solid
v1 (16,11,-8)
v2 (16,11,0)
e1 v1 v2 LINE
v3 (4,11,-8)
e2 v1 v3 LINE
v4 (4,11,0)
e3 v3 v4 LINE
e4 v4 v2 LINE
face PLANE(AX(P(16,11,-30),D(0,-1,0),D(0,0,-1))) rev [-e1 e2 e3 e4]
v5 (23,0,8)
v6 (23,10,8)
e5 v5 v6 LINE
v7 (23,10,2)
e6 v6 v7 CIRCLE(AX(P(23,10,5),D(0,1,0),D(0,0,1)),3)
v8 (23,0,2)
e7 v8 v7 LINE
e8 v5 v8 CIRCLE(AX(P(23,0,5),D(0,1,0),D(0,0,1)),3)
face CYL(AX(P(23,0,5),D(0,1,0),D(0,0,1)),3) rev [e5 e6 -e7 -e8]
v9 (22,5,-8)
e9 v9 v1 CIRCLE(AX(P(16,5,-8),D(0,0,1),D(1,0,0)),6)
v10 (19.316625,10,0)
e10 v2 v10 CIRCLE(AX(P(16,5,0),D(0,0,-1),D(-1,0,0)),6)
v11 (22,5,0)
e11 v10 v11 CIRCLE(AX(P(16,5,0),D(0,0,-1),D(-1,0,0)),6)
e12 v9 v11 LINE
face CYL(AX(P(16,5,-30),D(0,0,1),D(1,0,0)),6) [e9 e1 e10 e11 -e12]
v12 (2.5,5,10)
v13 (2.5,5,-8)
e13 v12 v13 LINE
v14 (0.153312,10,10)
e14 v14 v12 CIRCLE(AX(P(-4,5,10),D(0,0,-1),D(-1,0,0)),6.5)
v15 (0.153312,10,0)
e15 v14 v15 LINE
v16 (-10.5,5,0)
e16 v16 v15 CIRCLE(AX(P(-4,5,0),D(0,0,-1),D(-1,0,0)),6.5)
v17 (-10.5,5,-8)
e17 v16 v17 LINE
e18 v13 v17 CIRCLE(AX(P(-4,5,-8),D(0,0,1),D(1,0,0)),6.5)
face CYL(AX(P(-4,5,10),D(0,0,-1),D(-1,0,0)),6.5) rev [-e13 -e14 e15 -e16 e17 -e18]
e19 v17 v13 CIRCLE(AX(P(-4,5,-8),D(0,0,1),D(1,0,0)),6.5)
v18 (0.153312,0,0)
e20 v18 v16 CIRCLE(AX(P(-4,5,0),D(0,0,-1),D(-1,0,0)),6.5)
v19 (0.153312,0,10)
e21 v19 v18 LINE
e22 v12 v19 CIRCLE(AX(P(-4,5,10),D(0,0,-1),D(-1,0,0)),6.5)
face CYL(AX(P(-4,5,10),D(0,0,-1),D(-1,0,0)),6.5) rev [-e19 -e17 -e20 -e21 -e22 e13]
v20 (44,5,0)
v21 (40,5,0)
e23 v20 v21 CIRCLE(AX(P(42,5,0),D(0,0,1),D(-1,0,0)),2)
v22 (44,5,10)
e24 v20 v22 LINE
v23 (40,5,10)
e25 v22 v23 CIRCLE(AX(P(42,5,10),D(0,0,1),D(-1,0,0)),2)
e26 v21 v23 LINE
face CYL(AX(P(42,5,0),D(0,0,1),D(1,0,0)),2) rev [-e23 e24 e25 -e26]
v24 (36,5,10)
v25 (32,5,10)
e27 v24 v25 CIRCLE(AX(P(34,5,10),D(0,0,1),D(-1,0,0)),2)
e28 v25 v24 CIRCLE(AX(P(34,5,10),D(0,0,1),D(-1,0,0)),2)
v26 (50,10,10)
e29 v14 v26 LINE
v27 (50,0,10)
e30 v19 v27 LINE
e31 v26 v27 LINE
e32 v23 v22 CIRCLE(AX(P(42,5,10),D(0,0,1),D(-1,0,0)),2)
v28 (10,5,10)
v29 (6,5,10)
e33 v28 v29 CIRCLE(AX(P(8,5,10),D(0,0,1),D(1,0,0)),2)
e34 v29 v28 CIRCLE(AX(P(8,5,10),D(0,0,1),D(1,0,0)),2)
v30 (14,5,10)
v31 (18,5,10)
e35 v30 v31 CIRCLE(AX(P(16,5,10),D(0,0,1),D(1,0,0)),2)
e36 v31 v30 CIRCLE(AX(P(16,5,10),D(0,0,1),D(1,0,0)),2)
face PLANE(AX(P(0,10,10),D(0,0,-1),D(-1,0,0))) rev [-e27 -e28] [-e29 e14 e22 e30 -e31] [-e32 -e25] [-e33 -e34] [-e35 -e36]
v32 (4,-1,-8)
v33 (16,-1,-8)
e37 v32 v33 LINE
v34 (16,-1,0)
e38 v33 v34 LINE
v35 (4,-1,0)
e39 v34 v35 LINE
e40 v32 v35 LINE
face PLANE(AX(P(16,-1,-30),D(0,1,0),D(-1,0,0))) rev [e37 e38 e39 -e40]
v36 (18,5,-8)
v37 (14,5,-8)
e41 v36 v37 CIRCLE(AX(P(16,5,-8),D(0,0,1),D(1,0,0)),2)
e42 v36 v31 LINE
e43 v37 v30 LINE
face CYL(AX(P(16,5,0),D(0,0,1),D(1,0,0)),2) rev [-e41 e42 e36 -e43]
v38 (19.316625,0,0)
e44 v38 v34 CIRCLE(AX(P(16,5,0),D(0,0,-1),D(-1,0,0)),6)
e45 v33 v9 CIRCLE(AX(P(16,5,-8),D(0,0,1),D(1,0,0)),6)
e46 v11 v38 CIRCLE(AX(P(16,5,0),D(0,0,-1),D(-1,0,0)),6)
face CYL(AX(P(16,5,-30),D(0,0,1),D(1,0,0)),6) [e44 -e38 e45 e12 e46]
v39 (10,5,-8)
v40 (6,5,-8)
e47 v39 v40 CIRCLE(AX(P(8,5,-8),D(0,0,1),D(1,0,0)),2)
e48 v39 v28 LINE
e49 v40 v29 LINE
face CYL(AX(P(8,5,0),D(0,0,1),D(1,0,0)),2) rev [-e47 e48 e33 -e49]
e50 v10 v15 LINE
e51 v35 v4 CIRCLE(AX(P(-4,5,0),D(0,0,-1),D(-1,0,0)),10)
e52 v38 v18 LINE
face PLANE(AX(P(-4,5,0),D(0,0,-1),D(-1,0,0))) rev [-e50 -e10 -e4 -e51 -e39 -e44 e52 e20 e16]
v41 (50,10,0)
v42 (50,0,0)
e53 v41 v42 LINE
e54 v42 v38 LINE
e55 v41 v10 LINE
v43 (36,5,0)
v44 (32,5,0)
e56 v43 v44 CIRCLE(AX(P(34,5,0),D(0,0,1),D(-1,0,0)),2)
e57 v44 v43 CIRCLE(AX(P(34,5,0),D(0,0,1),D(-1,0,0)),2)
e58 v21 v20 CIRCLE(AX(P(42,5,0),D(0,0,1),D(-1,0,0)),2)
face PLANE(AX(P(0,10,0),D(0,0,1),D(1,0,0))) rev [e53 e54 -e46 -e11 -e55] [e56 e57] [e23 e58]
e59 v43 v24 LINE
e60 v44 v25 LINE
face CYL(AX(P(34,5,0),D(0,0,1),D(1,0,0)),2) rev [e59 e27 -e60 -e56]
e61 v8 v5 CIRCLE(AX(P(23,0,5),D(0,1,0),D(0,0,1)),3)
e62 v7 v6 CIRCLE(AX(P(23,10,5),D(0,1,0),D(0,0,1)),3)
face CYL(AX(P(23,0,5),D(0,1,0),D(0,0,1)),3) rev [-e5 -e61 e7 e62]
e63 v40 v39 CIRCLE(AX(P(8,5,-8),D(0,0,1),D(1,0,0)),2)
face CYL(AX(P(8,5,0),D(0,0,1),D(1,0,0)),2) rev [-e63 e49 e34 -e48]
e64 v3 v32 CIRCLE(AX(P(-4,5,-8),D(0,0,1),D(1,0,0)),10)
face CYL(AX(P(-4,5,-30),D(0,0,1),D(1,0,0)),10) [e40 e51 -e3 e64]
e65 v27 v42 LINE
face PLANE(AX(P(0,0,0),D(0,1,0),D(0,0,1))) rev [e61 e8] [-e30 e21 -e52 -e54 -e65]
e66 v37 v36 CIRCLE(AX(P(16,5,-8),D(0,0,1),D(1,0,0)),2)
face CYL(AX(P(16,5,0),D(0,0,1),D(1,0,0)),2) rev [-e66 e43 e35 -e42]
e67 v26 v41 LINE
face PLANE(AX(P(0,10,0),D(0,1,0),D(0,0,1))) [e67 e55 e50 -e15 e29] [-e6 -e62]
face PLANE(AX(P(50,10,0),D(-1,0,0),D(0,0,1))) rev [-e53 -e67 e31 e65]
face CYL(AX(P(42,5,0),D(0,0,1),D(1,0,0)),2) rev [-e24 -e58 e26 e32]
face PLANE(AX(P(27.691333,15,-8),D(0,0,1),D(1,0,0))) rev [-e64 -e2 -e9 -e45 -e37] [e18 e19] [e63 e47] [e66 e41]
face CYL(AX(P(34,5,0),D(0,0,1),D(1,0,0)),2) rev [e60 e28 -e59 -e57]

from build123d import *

# Parameters (mm, degrees)
SKETCH1_W               = 50
SKETCH1_H               = 10
BOSS_EXTRUDE1_DEPTH     = 10
SKETCH2_R               = 3
CUT_EXTRUDE1_DEPTH      = 10
SKETCH3_R               = 2
CUT_EXTRUDE2_DEPTH      = 10
BOSS_EXTRUDE2_DEPTH     = 30
CUT_EXTRUDE4_DEPTH      = 61.464865831
CUT_EXTRUDE4_DEPTH_BACK = 61.464865831
SKETCH6_W               = 47
SKETCH6_H               = 25
CUT_EXTRUDE5_DEPTH      = 54.150729064
CUT_EXTRUDE5_DEPTH_BACK = 54.150729064
SKETCH7_R               = 2
SKETCH5_R               = 6.5
CUT_EXTRUDE6_DEPTH      = 66.76473219


with BuildPart() as part:
    # Sketch1 → Boss-Extrude1 (new body)
    with BuildSketch(Plane(origin=(0, 0, 0), x_dir=(1, 0, 0), z_dir=(0, 1, 0))):
        with Locations((25, -5)):
            Rectangle(SKETCH1_W, SKETCH1_H)
    extrude(amount=BOSS_EXTRUDE1_DEPTH)

    # Sketch2 → Cut-Extrude1 (cut)
    with BuildSketch(Plane(origin=(0, 10, 0), x_dir=(1, 0, 0), z_dir=(0, 1, 0))):
        with Locations(Location((23, -5, 0), (0, 0, 270))):
            Circle(SKETCH2_R)
    extrude(amount=-CUT_EXTRUDE1_DEPTH, mode=Mode.SUBTRACT)

    # Sketch3 → Cut-Extrude2 (cut)
    with BuildSketch(Plane.XY.offset(10)):
        with Locations((8, 5)):
            Circle(SKETCH3_R)
        with Locations((16, 5)):
            Circle(SKETCH3_R)
        with Locations(Location((42, 5, 0), (0, 0, 180))):
            Circle(SKETCH3_R)
        with Locations(Location((34, 5, 0), (0, 0, 180))):
            Circle(SKETCH3_R)
    extrude(amount=-CUT_EXTRUDE2_DEPTH, mode=Mode.SUBTRACT)

    # Sketch4 → Boss-Extrude2 (add)
    with BuildSketch(Plane(origin=(0, 0, 0), x_dir=(-1, 0, 0), z_dir=(0, 0, -1))):
        with BuildLine():
            Line((-16, 11), (-4, 11))
            ThreePointArc((-4, 11), (14, 5), (-4, -1))
            Line((-4, -1), (-16, -1))
            ThreePointArc((-16, -1), (-22, 5), (-16, 11))
        make_face()
    extrude(amount=BOSS_EXTRUDE2_DEPTH)

    # Sketch6 → Cut-Extrude4 (cut, two sides: drawn at the far end of the back side and taken through both)
    with BuildSketch(Plane.XZ.offset(1).offset(-CUT_EXTRUDE4_DEPTH_BACK)):
        with Locations((4.191332745, -20.5)):
            Rectangle(SKETCH6_W, SKETCH6_H)
    extrude(amount=CUT_EXTRUDE4_DEPTH + CUT_EXTRUDE4_DEPTH_BACK, mode=Mode.SUBTRACT)

    # Sketch7 → Cut-Extrude5 (cut, two sides: drawn at the far end of the back side and taken through both)
    with BuildSketch(Plane.XY.offset(-CUT_EXTRUDE5_DEPTH_BACK)):
        with Locations((8, 5)):
            Circle(SKETCH7_R)
        with Locations((16, 5)):
            Circle(SKETCH7_R)
    extrude(amount=CUT_EXTRUDE5_DEPTH + CUT_EXTRUDE5_DEPTH_BACK, mode=Mode.SUBTRACT)

    # Sketch5 → Cut-Extrude6 (cut, through all)
    with BuildSketch(Plane(origin=(0, 0, -30), x_dir=(-1, 0, 0), z_dir=(0, 0, -1))):
        with Locations(Location((4, 5, 0), (0, 0, 230.284862768))):
            Circle(SKETCH5_R)
    extrude(amount=-CUT_EXTRUDE6_DEPTH, mode=Mode.SUBTRACT)


solid = part.part
